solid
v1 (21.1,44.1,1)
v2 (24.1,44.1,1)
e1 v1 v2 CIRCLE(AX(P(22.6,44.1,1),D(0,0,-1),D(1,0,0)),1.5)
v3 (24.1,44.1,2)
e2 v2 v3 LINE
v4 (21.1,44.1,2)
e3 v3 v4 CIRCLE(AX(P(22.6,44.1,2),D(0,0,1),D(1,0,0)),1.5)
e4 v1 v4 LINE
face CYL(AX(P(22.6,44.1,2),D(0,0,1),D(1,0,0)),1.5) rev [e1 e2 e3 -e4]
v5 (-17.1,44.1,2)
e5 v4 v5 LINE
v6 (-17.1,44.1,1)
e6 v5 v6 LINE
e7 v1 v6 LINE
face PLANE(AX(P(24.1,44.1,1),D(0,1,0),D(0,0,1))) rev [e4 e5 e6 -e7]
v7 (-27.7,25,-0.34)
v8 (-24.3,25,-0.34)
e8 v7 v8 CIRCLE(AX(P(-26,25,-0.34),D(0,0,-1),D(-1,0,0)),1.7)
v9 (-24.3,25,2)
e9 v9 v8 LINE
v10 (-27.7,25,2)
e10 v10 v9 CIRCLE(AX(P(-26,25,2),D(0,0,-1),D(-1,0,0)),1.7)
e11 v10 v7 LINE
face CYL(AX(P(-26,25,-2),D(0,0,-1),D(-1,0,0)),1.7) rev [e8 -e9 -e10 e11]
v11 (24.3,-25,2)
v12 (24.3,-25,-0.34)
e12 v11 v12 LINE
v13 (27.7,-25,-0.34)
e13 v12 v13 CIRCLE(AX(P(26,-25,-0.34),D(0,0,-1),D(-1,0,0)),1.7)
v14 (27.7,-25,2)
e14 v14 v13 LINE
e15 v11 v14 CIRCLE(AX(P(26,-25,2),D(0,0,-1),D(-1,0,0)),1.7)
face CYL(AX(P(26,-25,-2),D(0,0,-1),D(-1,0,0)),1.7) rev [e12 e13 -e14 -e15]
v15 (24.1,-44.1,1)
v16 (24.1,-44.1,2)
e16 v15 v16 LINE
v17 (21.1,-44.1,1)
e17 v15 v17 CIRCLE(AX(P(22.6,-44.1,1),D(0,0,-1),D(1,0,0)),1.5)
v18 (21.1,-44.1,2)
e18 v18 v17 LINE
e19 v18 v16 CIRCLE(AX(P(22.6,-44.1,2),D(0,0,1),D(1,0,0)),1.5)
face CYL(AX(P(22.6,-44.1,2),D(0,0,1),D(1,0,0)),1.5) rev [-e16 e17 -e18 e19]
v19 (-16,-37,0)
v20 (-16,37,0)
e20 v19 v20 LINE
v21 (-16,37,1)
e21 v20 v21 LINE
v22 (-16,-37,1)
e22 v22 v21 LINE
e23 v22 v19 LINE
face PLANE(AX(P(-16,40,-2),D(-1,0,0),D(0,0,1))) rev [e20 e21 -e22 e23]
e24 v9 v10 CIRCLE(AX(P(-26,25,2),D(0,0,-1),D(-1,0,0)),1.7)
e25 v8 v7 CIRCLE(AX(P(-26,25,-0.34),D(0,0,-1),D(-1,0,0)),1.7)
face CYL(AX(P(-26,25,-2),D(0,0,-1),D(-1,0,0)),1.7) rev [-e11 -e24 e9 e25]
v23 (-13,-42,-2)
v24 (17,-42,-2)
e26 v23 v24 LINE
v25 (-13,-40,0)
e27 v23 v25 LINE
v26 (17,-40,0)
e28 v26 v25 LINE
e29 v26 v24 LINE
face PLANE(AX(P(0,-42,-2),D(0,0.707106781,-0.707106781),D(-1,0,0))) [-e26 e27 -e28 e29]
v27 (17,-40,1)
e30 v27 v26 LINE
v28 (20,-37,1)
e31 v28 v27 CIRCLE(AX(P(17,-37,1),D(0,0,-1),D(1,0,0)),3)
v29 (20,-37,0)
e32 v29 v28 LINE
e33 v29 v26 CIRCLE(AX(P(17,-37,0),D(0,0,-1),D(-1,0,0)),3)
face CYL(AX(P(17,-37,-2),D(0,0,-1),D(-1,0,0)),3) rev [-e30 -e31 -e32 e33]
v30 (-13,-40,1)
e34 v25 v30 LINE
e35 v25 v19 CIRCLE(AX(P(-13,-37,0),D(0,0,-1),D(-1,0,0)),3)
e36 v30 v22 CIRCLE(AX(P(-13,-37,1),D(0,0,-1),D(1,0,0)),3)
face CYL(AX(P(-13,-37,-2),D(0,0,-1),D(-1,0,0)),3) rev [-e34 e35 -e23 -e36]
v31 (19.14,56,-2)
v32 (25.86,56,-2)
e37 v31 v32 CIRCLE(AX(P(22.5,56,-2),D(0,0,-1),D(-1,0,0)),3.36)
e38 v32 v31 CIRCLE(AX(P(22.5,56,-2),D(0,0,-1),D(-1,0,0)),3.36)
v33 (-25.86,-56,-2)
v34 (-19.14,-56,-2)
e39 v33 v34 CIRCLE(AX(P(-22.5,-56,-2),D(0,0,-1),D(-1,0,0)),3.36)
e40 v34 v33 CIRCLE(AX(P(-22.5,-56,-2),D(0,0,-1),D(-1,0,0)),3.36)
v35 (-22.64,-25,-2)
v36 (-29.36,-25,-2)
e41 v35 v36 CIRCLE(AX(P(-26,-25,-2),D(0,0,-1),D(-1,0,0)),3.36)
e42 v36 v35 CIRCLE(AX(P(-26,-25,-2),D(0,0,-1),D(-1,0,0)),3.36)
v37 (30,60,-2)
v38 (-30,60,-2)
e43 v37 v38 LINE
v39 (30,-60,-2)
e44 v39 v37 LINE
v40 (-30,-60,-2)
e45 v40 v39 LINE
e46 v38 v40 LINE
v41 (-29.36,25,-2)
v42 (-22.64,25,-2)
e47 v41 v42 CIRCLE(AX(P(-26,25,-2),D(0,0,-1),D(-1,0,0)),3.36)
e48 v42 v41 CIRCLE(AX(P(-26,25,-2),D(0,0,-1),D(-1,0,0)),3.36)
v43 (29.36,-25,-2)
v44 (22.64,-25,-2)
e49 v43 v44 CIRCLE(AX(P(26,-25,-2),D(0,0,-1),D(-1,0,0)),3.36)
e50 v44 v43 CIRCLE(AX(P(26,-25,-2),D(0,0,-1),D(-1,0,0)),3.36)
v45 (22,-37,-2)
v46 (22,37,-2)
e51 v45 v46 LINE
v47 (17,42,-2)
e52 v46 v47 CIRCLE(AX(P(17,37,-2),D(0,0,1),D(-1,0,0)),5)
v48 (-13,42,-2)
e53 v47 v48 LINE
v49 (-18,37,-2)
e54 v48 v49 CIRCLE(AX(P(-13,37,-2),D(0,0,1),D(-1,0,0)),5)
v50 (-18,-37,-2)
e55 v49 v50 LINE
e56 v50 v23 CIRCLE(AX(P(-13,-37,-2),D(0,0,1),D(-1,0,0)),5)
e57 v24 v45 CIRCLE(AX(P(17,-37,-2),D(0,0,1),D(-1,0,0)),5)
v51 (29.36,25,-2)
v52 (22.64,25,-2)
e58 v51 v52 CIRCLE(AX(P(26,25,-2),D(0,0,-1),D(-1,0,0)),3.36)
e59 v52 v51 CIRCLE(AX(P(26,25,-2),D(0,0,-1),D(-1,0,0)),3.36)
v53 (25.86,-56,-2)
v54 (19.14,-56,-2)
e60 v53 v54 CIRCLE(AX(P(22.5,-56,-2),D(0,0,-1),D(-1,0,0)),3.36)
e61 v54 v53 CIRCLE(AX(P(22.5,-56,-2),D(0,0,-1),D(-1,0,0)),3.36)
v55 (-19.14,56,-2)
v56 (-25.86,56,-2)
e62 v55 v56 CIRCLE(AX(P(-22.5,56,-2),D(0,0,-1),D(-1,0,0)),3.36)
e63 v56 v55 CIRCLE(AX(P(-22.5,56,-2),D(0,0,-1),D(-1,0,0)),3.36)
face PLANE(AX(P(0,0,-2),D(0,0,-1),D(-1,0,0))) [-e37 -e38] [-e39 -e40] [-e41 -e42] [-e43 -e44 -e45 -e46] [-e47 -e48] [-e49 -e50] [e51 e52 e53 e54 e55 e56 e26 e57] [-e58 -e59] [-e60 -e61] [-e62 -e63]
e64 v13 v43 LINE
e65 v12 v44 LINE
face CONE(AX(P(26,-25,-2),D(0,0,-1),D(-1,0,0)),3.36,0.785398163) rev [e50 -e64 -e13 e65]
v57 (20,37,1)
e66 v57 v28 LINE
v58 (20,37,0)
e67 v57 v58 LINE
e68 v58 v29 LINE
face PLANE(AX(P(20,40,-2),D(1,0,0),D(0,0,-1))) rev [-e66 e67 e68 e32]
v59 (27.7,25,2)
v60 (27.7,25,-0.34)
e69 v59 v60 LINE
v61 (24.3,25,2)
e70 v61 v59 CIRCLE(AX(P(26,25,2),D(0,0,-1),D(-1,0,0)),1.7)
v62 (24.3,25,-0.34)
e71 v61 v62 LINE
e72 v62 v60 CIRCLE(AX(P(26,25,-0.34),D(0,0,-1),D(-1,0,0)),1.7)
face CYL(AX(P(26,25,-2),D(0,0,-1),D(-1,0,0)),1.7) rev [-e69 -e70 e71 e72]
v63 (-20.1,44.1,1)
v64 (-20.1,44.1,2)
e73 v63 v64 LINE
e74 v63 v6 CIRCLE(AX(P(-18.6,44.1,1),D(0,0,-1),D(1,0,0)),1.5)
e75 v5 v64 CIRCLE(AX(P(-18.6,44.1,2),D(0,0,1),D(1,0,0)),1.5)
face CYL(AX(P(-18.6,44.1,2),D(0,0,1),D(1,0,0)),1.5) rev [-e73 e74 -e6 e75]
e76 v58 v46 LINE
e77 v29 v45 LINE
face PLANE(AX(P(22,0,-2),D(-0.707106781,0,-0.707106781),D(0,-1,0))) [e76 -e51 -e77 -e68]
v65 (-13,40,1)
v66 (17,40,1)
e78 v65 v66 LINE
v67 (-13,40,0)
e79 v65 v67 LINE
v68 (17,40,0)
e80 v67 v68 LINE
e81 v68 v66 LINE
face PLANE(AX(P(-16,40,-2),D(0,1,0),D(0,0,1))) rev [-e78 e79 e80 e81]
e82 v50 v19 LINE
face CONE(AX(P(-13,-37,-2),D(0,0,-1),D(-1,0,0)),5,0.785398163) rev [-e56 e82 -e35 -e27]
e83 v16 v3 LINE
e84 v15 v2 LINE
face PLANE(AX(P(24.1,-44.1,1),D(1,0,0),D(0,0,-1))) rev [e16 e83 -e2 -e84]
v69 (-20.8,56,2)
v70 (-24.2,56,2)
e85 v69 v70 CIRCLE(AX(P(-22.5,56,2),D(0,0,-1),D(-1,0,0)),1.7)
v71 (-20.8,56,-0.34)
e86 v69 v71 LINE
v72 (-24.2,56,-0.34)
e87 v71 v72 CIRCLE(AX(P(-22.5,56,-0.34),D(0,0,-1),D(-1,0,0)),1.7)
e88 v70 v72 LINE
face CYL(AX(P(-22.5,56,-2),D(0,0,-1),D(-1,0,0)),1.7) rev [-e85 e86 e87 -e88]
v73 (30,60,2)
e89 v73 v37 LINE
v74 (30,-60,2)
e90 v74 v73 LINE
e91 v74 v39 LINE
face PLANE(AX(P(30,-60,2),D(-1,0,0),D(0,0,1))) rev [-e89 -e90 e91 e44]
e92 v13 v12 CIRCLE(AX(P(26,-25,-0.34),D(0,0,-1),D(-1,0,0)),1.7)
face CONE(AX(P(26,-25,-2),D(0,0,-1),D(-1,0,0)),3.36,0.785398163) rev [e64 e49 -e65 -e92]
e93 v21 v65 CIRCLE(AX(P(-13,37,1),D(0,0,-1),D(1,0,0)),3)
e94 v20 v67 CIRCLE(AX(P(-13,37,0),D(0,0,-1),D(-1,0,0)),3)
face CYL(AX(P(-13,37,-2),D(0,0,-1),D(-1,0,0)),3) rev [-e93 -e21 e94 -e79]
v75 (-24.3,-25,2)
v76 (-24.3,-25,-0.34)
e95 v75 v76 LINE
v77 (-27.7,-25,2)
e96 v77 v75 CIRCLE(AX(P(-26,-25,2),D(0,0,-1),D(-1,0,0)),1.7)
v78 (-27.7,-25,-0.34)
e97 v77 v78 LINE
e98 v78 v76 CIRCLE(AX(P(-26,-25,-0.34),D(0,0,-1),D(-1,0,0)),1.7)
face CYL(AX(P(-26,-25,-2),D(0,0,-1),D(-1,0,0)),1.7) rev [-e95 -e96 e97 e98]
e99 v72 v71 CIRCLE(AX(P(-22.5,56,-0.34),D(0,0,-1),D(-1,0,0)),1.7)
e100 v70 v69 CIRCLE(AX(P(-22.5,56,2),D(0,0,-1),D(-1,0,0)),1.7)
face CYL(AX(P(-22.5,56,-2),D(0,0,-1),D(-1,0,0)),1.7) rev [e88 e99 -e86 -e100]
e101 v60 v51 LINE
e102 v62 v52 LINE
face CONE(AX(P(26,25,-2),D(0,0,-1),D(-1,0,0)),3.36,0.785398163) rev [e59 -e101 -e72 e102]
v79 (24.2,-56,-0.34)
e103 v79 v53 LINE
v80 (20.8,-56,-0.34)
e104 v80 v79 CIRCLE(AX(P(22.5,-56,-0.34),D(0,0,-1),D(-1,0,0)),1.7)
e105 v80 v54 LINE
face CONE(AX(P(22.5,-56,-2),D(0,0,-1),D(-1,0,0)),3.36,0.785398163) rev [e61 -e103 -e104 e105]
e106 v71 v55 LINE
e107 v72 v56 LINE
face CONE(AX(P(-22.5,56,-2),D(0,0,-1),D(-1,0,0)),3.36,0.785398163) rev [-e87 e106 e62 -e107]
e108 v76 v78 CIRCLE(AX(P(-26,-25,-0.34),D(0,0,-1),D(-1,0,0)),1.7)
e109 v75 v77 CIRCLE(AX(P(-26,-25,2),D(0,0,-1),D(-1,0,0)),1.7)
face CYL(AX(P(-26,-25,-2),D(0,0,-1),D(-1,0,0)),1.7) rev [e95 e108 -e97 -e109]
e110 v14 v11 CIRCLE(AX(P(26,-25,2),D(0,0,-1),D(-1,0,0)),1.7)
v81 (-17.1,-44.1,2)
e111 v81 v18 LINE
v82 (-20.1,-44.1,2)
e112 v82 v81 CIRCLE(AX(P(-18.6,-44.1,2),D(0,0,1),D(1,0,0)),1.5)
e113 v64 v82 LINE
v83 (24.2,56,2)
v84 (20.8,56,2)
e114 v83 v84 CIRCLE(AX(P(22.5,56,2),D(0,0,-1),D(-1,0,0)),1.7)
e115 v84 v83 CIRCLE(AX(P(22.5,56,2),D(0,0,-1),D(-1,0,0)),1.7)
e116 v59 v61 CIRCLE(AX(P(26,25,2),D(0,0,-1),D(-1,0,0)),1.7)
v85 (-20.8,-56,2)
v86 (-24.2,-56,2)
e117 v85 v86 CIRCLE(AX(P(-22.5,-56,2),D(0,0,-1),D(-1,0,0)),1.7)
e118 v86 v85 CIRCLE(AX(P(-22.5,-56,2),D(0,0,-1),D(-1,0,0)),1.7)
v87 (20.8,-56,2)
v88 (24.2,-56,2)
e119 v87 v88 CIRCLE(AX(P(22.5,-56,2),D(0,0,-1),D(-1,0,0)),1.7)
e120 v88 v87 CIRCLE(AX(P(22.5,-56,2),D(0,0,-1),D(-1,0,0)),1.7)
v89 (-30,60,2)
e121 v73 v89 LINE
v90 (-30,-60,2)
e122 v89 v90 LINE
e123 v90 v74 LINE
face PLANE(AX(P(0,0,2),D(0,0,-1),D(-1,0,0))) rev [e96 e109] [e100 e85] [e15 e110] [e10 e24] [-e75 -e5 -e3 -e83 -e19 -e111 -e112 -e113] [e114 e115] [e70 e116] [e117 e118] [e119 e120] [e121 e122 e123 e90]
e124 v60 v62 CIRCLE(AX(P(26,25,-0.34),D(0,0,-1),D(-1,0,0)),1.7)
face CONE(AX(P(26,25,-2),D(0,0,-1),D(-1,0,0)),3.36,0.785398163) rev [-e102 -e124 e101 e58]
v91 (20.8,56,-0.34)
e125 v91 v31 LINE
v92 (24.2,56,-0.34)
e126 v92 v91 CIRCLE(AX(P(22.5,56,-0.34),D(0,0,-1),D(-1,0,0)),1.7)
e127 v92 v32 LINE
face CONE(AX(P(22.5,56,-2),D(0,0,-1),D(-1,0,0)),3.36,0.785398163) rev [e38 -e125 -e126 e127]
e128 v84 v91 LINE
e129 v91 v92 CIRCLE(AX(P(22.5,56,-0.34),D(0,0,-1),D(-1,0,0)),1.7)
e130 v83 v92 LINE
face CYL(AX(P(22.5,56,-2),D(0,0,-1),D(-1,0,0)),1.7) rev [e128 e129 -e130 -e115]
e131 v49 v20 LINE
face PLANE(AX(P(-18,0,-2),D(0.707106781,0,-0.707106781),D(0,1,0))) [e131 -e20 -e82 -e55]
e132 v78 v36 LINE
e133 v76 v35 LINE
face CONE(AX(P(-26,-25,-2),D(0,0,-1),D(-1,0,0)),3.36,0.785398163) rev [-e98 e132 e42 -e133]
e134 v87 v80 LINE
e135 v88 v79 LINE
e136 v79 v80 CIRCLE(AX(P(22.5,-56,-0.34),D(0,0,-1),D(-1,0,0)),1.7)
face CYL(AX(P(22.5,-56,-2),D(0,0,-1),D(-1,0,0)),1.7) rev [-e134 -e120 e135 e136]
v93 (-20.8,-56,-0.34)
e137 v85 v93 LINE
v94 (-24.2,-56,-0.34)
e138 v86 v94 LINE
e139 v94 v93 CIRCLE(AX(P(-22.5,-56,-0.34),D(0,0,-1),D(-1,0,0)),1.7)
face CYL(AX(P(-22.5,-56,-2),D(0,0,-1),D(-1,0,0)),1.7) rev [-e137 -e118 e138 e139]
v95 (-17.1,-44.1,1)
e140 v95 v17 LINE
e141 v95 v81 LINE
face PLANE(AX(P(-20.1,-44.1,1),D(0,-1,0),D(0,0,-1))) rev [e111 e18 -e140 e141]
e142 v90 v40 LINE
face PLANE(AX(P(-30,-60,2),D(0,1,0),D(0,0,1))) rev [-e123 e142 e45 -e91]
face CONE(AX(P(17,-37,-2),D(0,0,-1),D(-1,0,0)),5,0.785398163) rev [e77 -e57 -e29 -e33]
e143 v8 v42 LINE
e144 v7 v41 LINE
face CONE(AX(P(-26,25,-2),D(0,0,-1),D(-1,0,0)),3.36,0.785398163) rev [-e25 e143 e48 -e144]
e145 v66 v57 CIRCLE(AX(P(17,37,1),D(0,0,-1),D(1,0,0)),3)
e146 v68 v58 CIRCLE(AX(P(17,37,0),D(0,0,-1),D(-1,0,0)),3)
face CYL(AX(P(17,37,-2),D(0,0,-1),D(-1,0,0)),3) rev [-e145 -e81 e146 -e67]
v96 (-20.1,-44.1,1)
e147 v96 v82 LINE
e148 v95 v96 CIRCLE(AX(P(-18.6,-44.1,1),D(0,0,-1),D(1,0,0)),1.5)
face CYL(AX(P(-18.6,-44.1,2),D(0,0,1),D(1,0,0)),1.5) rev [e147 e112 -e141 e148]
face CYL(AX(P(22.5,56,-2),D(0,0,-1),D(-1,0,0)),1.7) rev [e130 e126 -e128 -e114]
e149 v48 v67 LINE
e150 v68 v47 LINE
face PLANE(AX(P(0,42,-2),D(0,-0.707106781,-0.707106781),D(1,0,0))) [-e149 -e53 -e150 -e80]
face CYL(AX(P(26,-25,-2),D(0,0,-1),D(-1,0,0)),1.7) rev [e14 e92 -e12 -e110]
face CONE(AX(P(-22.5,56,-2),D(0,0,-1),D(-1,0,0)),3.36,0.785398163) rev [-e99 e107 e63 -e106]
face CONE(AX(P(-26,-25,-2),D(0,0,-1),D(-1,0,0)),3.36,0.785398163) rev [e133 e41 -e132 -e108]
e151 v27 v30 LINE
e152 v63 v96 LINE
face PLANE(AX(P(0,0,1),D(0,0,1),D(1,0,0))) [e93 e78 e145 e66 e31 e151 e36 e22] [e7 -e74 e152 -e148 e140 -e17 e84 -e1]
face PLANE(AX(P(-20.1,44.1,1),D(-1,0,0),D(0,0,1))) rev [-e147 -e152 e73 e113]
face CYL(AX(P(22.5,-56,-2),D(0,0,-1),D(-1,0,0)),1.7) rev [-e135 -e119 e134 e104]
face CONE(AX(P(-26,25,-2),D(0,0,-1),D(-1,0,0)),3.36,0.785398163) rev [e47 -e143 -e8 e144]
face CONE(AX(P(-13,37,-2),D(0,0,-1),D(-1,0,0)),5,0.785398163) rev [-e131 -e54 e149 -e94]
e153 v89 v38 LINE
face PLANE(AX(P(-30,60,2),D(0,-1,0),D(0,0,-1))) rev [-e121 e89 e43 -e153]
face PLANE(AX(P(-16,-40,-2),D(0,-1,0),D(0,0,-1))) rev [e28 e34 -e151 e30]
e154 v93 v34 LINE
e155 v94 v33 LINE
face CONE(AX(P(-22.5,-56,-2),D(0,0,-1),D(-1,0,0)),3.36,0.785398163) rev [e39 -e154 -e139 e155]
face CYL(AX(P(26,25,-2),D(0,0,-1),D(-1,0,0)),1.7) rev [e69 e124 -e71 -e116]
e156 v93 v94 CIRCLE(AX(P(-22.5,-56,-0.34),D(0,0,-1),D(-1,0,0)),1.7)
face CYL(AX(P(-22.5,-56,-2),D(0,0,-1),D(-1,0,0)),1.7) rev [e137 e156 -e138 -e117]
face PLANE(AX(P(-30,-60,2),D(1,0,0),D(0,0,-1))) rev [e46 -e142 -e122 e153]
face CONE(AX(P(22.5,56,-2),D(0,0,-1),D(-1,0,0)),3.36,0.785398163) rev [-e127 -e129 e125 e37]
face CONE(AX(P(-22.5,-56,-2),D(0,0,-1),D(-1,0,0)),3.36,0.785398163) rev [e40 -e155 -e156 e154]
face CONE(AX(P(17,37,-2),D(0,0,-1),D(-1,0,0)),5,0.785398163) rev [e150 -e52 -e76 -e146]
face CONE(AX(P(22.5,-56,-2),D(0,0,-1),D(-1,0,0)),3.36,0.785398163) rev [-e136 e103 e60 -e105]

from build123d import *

# Parameters (mm, degrees)
SKETCH_1_W                   = 60
SKETCH_1_H                   = 120
EXTRUDE_1_DEPTH              = 2
SKETCH_2_W                   = 36
SKETCH_2_H                   = 80
CUT_EXTRUDE_1_DEPTH          = 68.201190466
SKETCH_3_W                   = 44.2
SKETCH_3_H                   = 88.2
CUT_EXTRUDE_2_DEPTH          = 1
HOLE_WIZARD_3_0_3_1_D        = 3
HOLE_WIZARD_3_0_3_1_DEPTH    = 1
FILLET_1_R                   = 3
CHAMFER_1_SIZE               = 2
HOLE_WIZARD_M3_1_D           = 3.4
HOLE_WIZARD_M3_1_CSINK_D     = 6.72
HOLE_WIZARD_M3_1_CSINK_ANGLE = 90


with BuildPart() as part:
    # 草图1 → 凸台-拉伸1 (new, symmetric)
    with BuildSketch(Plane.XY):
        Rectangle(SKETCH_1_W, SKETCH_1_H)
    extrude(amount=EXTRUDE_1_DEPTH, both=True)

    # 草图2 → 切除-拉伸1 (cut, through all)
    with BuildSketch(Plane.XY.offset(2)):
        with Locations((2, 0)):
            Rectangle(SKETCH_2_W, SKETCH_2_H)
    extrude(amount=-CUT_EXTRUDE_1_DEPTH, mode=Mode.SUBTRACT)

    # 草图3 → 切除-拉伸2 (cut)
    with BuildSketch(Plane.XY.offset(2)):
        with Locations((2, 0)):
            Rectangle(SKETCH_3_W, SKETCH_3_H)
    extrude(amount=-CUT_EXTRUDE_2_DEPTH, mode=Mode.SUBTRACT)

    # Ø3.0 (3) 直径孔1
    with Locations(Plane.XY.offset(2)):
        with Locations((-18.6, 44.1), (22.6, 44.1), (22.6, -44.1), (-18.6, -44.1)):
            Hole(HOLE_WIZARD_3_0_3_1_D / 2, depth=HOLE_WIZARD_3_0_3_1_DEPTH)

    # 圆角1
    fillet_1_edges = [part.edges().sort_by_distance(p)[0] for p in [
        (-16, -40, -0.5),
        (-16, 40, -0.5),
        (20, 40, -0.5),
        (20, -40, -0.5),
    ]]
    fillet(fillet_1_edges, radius=FILLET_1_R)

    # 倒角1
    chamfer_1_edges = [part.edges().sort_by_distance(p)[0] for p in [
        (20, 0, -2),
        (2, -40, -2),
        (-16, 0, -2),
        (19.121320344, 39.121320344, -2),
        (19.121320344, -39.121320344, -2),
        (-15.121320344, -39.121320344, -2),
        (-15.121320344, 39.121320344, -2),
        (2, 40, -2),
    ]]
    chamfer(chamfer_1_edges, length=CHAMFER_1_SIZE)

    # M3 六角凹锥坑螺钉的锥形沉头孔1 (through all)
    with Locations(Plane(origin=(0, 0, -2), x_dir=(-1, 0, 0), z_dir=(0, 0, -1))):
        with Locations((-22.5, 56), (22.5, 56), (26, 25), (26, -25), (22.5, -56), (-22.5, -56), (-26, -25), (-26, 25)):
            CounterSinkHole(HOLE_WIZARD_M3_1_D / 2, HOLE_WIZARD_M3_1_CSINK_D / 2, counter_sink_angle=HOLE_WIZARD_M3_1_CSINK_ANGLE)


solid = part.part
